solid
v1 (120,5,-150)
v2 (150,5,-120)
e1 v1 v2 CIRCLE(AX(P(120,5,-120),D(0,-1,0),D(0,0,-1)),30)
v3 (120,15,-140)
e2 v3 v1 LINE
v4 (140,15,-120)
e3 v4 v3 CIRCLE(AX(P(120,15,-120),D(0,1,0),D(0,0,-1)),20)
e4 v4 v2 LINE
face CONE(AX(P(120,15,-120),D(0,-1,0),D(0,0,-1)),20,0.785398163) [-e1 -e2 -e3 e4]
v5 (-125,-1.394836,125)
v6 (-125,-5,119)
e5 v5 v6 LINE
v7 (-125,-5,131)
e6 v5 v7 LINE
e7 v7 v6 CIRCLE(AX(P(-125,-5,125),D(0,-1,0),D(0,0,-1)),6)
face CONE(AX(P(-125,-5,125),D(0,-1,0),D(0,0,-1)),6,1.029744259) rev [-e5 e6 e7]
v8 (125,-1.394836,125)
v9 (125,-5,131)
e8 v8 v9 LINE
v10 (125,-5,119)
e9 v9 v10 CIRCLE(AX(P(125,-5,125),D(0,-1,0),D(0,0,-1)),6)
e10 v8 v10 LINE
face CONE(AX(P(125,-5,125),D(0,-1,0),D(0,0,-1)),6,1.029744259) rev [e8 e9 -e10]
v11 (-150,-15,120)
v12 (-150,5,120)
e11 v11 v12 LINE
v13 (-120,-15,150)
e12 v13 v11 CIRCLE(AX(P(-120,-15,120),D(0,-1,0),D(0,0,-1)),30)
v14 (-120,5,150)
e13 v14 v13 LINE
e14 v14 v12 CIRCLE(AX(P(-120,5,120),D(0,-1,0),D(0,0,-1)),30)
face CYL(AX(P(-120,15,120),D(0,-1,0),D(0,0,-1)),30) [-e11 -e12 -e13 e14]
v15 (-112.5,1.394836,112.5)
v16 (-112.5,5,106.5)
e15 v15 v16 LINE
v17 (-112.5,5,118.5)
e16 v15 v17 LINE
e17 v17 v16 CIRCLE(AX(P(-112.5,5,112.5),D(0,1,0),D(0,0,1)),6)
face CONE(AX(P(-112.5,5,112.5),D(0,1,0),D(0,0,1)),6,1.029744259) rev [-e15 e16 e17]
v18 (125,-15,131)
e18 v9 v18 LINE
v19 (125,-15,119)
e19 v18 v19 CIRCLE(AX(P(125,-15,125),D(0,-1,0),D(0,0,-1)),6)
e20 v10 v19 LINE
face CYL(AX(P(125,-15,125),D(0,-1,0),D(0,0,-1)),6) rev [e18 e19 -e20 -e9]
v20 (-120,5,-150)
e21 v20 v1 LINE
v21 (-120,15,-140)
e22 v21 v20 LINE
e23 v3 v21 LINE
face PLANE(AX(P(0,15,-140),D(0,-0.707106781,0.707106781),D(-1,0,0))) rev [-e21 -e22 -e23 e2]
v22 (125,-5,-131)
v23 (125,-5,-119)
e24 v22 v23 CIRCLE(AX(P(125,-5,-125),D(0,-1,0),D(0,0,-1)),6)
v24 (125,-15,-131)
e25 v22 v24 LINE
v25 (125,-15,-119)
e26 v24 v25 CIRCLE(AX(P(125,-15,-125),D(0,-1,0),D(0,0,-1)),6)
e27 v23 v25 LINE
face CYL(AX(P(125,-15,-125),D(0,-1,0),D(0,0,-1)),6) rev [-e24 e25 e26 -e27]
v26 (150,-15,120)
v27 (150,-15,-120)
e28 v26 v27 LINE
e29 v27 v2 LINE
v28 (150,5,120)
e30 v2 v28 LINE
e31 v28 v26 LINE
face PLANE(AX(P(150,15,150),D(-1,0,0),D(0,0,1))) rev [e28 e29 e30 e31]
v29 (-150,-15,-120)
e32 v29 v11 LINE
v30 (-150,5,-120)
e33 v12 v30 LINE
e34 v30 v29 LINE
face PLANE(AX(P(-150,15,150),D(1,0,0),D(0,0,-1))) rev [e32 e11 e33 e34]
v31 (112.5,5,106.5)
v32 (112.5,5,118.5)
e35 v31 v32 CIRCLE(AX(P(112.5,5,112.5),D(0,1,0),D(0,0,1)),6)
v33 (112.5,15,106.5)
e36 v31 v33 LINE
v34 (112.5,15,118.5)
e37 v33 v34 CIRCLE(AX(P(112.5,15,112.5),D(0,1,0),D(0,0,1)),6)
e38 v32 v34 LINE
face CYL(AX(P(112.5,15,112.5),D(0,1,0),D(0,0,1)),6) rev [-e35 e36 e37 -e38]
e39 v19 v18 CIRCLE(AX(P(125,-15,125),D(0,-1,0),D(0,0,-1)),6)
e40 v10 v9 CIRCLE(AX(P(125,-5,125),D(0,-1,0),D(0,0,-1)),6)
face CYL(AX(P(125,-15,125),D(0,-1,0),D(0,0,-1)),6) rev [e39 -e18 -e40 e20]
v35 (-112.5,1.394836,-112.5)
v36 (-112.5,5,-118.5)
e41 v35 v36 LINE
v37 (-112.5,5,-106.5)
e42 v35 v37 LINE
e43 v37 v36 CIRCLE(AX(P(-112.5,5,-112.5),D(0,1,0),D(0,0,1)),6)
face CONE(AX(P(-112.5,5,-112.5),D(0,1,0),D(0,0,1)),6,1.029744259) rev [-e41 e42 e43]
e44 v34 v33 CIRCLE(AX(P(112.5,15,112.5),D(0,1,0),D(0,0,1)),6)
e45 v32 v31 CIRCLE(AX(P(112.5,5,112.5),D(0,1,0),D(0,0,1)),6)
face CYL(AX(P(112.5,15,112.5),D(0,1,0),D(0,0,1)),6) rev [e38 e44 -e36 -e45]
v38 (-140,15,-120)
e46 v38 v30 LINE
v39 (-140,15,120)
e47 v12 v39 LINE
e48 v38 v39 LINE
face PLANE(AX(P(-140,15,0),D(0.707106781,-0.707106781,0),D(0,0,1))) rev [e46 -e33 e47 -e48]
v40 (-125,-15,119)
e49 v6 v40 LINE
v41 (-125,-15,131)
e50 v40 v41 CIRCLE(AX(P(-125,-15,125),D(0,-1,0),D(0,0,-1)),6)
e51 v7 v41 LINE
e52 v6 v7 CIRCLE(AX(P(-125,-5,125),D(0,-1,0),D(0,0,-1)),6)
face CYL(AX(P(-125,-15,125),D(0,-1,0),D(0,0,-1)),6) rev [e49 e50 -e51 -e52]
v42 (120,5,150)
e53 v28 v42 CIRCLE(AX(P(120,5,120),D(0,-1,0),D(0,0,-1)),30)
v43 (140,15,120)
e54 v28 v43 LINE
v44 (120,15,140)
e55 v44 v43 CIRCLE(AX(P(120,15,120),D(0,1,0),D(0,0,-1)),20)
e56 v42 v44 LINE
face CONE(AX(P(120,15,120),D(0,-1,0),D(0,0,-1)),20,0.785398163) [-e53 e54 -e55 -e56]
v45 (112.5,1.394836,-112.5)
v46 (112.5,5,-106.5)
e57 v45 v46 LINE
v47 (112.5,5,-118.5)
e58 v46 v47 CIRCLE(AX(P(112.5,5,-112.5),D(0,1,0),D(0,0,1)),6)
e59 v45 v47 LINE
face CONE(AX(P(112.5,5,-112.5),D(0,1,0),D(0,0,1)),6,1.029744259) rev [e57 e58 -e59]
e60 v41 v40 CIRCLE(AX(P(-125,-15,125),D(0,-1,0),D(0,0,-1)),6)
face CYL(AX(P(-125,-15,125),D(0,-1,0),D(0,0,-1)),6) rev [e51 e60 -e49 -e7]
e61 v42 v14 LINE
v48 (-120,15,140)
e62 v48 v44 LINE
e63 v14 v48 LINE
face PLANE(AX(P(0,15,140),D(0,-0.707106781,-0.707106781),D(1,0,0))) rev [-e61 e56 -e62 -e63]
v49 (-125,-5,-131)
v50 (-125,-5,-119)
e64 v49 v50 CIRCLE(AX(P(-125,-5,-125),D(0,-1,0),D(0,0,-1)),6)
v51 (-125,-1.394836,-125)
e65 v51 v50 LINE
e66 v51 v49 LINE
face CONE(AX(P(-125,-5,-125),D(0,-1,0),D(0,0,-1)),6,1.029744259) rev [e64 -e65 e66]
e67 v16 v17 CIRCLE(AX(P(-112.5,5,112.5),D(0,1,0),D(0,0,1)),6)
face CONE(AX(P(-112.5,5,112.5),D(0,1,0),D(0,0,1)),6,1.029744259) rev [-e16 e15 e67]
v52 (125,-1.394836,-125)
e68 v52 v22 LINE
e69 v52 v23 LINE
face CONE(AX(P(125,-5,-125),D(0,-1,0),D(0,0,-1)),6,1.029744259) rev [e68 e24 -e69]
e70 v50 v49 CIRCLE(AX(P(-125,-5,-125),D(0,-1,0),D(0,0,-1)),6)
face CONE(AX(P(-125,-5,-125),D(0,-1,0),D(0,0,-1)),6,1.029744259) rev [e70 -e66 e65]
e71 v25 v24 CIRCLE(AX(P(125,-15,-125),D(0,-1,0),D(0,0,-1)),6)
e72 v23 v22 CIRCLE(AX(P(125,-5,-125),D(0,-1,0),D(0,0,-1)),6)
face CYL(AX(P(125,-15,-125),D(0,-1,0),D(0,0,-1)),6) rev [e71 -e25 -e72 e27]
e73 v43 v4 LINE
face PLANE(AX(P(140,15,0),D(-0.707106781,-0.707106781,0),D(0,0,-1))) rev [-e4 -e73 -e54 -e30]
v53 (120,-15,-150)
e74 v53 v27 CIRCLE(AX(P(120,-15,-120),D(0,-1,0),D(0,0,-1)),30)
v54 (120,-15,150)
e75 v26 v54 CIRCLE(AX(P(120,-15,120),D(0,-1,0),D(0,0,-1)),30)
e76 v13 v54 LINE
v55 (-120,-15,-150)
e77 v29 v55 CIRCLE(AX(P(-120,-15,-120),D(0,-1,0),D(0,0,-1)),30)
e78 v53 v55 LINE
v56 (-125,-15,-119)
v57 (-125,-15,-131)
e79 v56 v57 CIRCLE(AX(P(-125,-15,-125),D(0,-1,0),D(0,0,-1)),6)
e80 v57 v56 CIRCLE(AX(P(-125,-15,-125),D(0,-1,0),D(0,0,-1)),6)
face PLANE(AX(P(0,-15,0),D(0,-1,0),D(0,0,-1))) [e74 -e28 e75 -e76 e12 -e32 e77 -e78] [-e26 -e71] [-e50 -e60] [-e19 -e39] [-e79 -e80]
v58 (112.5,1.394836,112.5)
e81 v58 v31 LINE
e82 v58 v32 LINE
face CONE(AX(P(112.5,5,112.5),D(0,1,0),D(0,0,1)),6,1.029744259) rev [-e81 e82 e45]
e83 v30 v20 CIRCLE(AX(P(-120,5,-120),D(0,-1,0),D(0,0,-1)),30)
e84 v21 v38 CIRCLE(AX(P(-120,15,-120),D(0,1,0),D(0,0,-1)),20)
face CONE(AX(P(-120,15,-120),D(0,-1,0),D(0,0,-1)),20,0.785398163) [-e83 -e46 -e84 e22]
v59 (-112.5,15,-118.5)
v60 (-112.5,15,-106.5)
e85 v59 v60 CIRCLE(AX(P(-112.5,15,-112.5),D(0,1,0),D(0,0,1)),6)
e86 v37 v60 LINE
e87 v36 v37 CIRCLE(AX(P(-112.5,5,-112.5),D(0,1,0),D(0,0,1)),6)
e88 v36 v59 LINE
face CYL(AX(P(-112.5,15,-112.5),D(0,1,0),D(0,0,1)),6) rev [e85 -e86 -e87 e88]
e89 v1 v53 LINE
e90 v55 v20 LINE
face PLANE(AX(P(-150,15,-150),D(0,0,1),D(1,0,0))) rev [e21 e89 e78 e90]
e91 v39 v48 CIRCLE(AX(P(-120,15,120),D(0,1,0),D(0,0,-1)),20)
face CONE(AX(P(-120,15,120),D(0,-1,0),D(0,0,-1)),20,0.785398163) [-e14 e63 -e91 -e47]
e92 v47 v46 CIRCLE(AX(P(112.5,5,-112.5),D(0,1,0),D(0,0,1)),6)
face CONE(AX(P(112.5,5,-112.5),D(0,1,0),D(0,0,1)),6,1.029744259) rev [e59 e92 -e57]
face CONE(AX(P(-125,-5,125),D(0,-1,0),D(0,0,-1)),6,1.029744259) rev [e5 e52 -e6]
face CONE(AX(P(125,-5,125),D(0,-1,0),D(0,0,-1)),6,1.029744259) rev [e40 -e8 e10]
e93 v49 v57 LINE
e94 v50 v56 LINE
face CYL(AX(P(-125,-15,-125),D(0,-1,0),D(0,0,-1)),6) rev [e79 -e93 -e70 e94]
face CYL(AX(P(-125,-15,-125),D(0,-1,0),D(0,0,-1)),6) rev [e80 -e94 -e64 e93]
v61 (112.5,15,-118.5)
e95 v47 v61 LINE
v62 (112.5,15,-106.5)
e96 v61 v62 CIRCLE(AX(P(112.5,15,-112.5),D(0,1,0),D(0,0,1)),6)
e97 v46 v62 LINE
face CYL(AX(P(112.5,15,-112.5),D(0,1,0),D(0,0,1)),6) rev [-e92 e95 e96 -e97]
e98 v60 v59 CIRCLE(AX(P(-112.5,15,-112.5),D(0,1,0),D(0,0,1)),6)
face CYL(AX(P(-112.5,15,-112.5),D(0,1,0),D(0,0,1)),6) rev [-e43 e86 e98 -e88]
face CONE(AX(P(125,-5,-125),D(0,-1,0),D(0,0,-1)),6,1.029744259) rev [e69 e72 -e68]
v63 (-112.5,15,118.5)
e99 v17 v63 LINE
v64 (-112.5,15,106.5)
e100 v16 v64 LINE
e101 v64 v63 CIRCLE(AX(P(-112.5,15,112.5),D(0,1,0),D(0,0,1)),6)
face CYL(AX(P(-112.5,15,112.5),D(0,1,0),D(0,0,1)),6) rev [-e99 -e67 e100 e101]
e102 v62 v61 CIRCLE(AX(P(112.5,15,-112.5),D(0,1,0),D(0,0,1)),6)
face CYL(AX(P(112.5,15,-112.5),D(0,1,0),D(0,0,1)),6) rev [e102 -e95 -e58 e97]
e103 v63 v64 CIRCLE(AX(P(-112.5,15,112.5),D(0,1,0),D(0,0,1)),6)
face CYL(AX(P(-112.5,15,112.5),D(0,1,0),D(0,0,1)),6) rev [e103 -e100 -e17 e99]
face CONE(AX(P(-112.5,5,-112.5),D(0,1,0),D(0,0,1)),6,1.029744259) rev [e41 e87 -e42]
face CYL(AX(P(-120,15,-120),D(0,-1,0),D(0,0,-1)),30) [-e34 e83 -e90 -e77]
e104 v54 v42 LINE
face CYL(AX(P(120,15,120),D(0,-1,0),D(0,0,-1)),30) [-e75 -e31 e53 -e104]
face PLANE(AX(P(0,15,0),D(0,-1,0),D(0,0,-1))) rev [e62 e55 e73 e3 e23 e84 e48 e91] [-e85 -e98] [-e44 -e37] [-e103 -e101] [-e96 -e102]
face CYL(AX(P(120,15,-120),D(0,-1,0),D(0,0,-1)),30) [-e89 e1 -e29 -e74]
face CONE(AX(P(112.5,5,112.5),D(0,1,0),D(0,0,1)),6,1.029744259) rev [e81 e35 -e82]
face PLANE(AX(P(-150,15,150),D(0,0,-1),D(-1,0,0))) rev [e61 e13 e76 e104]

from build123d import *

# Parameters (mm, degrees)
BASE_PLATE_PROFILE_300X300_W       = 300
BASE_PLATE_PROFILE_300X300_H       = 300
BASE_PLATE_300X300X30_DEPTH        = 15
CORNER_FILLETS_R30_R               = 30
EDGE_CHAMFER_10X45_SIZE            = 10
DOWEL_HOLES_12_ON_225_SQUARE_D     = 12
DOWEL_HOLES_12_ON_225_SQUARE_DEPTH = 10
DOWEL_HOLES_12_ON_225_SQUARE_TIP   = 3.605163714
DOWEL_HOLES_12_ON_250_SQUARE_D     = 12
DOWEL_HOLES_12_ON_250_SQUARE_DEPTH = 10
DOWEL_HOLES_12_ON_250_SQUARE_TIP   = 3.605163714


with BuildPart() as part:
    # Base Plate Profile 300x300 → Base Plate 300x300x30 (new, symmetric)
    with BuildSketch(Plane(origin=(0, 0, 0), x_dir=(1, 0, 0), z_dir=(0, 1, 0))):
        Rectangle(BASE_PLATE_PROFILE_300X300_W, BASE_PLATE_PROFILE_300X300_H)
    extrude(amount=BASE_PLATE_300X300X30_DEPTH, both=True)

    # Corner Fillets R30
    corner_fillets_r30_edges = [part.edges().sort_by_distance(p)[0] for p in [
        (150, 0, 150),
        (-150, 0, 150),
        (-150, 0, -150),
        (150, 0, -150),
    ]]
    fillet(corner_fillets_r30_edges, radius=CORNER_FILLETS_R30_R)

    # Edge Chamfer 10x45
    edge_chamfer_10x45_edges = [part.edges().sort_by_distance(p)[0] for p in [
        (0, 15, 150),
        (-150, 15, 0),
        (150, 15, 0),
        (0, 15, -150),
        (141.213203436, 15, -141.213203436),
        (-141.213203436, 15, -141.213203436),
        (141.213203436, 15, 141.213203436),
        (-141.213203436, 15, 141.213203436),
    ]]
    chamfer(edge_chamfer_10x45_edges, length=EDGE_CHAMFER_10X45_SIZE)

    # Dowel Holes Ø12 on 225 Square
    with Locations(Plane(origin=(112.5, 15, -112.5), x_dir=(0, 0, 1), z_dir=(0, 1, 0))):
        with Locations((0, 0), (0, -225), (225, -225), (225, 0)):
            Hole(DOWEL_HOLES_12_ON_225_SQUARE_D / 2, depth=DOWEL_HOLES_12_ON_225_SQUARE_DEPTH)
            with Locations((0, 0, -(DOWEL_HOLES_12_ON_225_SQUARE_DEPTH + DOWEL_HOLES_12_ON_225_SQUARE_TIP / 2))):  # 118° drill point
                Cone(0, DOWEL_HOLES_12_ON_225_SQUARE_D / 2, DOWEL_HOLES_12_ON_225_SQUARE_TIP, mode=Mode.SUBTRACT)

    # Dowel Holes Ø12 on 250 Square
    with Locations(Plane(origin=(-125, -15, 125), x_dir=(0, 0, -1), z_dir=(0, -1, 0))):
        with Locations((0, 0), (0, 250), (250, 250), (250, 0)):
            Hole(DOWEL_HOLES_12_ON_250_SQUARE_D / 2, depth=DOWEL_HOLES_12_ON_250_SQUARE_DEPTH)
            with Locations((0, 0, -(DOWEL_HOLES_12_ON_250_SQUARE_DEPTH + DOWEL_HOLES_12_ON_250_SQUARE_TIP / 2))):  # 118° drill point
                Cone(0, DOWEL_HOLES_12_ON_250_SQUARE_D / 2, DOWEL_HOLES_12_ON_250_SQUARE_TIP, mode=Mode.SUBTRACT)


solid = part.part
